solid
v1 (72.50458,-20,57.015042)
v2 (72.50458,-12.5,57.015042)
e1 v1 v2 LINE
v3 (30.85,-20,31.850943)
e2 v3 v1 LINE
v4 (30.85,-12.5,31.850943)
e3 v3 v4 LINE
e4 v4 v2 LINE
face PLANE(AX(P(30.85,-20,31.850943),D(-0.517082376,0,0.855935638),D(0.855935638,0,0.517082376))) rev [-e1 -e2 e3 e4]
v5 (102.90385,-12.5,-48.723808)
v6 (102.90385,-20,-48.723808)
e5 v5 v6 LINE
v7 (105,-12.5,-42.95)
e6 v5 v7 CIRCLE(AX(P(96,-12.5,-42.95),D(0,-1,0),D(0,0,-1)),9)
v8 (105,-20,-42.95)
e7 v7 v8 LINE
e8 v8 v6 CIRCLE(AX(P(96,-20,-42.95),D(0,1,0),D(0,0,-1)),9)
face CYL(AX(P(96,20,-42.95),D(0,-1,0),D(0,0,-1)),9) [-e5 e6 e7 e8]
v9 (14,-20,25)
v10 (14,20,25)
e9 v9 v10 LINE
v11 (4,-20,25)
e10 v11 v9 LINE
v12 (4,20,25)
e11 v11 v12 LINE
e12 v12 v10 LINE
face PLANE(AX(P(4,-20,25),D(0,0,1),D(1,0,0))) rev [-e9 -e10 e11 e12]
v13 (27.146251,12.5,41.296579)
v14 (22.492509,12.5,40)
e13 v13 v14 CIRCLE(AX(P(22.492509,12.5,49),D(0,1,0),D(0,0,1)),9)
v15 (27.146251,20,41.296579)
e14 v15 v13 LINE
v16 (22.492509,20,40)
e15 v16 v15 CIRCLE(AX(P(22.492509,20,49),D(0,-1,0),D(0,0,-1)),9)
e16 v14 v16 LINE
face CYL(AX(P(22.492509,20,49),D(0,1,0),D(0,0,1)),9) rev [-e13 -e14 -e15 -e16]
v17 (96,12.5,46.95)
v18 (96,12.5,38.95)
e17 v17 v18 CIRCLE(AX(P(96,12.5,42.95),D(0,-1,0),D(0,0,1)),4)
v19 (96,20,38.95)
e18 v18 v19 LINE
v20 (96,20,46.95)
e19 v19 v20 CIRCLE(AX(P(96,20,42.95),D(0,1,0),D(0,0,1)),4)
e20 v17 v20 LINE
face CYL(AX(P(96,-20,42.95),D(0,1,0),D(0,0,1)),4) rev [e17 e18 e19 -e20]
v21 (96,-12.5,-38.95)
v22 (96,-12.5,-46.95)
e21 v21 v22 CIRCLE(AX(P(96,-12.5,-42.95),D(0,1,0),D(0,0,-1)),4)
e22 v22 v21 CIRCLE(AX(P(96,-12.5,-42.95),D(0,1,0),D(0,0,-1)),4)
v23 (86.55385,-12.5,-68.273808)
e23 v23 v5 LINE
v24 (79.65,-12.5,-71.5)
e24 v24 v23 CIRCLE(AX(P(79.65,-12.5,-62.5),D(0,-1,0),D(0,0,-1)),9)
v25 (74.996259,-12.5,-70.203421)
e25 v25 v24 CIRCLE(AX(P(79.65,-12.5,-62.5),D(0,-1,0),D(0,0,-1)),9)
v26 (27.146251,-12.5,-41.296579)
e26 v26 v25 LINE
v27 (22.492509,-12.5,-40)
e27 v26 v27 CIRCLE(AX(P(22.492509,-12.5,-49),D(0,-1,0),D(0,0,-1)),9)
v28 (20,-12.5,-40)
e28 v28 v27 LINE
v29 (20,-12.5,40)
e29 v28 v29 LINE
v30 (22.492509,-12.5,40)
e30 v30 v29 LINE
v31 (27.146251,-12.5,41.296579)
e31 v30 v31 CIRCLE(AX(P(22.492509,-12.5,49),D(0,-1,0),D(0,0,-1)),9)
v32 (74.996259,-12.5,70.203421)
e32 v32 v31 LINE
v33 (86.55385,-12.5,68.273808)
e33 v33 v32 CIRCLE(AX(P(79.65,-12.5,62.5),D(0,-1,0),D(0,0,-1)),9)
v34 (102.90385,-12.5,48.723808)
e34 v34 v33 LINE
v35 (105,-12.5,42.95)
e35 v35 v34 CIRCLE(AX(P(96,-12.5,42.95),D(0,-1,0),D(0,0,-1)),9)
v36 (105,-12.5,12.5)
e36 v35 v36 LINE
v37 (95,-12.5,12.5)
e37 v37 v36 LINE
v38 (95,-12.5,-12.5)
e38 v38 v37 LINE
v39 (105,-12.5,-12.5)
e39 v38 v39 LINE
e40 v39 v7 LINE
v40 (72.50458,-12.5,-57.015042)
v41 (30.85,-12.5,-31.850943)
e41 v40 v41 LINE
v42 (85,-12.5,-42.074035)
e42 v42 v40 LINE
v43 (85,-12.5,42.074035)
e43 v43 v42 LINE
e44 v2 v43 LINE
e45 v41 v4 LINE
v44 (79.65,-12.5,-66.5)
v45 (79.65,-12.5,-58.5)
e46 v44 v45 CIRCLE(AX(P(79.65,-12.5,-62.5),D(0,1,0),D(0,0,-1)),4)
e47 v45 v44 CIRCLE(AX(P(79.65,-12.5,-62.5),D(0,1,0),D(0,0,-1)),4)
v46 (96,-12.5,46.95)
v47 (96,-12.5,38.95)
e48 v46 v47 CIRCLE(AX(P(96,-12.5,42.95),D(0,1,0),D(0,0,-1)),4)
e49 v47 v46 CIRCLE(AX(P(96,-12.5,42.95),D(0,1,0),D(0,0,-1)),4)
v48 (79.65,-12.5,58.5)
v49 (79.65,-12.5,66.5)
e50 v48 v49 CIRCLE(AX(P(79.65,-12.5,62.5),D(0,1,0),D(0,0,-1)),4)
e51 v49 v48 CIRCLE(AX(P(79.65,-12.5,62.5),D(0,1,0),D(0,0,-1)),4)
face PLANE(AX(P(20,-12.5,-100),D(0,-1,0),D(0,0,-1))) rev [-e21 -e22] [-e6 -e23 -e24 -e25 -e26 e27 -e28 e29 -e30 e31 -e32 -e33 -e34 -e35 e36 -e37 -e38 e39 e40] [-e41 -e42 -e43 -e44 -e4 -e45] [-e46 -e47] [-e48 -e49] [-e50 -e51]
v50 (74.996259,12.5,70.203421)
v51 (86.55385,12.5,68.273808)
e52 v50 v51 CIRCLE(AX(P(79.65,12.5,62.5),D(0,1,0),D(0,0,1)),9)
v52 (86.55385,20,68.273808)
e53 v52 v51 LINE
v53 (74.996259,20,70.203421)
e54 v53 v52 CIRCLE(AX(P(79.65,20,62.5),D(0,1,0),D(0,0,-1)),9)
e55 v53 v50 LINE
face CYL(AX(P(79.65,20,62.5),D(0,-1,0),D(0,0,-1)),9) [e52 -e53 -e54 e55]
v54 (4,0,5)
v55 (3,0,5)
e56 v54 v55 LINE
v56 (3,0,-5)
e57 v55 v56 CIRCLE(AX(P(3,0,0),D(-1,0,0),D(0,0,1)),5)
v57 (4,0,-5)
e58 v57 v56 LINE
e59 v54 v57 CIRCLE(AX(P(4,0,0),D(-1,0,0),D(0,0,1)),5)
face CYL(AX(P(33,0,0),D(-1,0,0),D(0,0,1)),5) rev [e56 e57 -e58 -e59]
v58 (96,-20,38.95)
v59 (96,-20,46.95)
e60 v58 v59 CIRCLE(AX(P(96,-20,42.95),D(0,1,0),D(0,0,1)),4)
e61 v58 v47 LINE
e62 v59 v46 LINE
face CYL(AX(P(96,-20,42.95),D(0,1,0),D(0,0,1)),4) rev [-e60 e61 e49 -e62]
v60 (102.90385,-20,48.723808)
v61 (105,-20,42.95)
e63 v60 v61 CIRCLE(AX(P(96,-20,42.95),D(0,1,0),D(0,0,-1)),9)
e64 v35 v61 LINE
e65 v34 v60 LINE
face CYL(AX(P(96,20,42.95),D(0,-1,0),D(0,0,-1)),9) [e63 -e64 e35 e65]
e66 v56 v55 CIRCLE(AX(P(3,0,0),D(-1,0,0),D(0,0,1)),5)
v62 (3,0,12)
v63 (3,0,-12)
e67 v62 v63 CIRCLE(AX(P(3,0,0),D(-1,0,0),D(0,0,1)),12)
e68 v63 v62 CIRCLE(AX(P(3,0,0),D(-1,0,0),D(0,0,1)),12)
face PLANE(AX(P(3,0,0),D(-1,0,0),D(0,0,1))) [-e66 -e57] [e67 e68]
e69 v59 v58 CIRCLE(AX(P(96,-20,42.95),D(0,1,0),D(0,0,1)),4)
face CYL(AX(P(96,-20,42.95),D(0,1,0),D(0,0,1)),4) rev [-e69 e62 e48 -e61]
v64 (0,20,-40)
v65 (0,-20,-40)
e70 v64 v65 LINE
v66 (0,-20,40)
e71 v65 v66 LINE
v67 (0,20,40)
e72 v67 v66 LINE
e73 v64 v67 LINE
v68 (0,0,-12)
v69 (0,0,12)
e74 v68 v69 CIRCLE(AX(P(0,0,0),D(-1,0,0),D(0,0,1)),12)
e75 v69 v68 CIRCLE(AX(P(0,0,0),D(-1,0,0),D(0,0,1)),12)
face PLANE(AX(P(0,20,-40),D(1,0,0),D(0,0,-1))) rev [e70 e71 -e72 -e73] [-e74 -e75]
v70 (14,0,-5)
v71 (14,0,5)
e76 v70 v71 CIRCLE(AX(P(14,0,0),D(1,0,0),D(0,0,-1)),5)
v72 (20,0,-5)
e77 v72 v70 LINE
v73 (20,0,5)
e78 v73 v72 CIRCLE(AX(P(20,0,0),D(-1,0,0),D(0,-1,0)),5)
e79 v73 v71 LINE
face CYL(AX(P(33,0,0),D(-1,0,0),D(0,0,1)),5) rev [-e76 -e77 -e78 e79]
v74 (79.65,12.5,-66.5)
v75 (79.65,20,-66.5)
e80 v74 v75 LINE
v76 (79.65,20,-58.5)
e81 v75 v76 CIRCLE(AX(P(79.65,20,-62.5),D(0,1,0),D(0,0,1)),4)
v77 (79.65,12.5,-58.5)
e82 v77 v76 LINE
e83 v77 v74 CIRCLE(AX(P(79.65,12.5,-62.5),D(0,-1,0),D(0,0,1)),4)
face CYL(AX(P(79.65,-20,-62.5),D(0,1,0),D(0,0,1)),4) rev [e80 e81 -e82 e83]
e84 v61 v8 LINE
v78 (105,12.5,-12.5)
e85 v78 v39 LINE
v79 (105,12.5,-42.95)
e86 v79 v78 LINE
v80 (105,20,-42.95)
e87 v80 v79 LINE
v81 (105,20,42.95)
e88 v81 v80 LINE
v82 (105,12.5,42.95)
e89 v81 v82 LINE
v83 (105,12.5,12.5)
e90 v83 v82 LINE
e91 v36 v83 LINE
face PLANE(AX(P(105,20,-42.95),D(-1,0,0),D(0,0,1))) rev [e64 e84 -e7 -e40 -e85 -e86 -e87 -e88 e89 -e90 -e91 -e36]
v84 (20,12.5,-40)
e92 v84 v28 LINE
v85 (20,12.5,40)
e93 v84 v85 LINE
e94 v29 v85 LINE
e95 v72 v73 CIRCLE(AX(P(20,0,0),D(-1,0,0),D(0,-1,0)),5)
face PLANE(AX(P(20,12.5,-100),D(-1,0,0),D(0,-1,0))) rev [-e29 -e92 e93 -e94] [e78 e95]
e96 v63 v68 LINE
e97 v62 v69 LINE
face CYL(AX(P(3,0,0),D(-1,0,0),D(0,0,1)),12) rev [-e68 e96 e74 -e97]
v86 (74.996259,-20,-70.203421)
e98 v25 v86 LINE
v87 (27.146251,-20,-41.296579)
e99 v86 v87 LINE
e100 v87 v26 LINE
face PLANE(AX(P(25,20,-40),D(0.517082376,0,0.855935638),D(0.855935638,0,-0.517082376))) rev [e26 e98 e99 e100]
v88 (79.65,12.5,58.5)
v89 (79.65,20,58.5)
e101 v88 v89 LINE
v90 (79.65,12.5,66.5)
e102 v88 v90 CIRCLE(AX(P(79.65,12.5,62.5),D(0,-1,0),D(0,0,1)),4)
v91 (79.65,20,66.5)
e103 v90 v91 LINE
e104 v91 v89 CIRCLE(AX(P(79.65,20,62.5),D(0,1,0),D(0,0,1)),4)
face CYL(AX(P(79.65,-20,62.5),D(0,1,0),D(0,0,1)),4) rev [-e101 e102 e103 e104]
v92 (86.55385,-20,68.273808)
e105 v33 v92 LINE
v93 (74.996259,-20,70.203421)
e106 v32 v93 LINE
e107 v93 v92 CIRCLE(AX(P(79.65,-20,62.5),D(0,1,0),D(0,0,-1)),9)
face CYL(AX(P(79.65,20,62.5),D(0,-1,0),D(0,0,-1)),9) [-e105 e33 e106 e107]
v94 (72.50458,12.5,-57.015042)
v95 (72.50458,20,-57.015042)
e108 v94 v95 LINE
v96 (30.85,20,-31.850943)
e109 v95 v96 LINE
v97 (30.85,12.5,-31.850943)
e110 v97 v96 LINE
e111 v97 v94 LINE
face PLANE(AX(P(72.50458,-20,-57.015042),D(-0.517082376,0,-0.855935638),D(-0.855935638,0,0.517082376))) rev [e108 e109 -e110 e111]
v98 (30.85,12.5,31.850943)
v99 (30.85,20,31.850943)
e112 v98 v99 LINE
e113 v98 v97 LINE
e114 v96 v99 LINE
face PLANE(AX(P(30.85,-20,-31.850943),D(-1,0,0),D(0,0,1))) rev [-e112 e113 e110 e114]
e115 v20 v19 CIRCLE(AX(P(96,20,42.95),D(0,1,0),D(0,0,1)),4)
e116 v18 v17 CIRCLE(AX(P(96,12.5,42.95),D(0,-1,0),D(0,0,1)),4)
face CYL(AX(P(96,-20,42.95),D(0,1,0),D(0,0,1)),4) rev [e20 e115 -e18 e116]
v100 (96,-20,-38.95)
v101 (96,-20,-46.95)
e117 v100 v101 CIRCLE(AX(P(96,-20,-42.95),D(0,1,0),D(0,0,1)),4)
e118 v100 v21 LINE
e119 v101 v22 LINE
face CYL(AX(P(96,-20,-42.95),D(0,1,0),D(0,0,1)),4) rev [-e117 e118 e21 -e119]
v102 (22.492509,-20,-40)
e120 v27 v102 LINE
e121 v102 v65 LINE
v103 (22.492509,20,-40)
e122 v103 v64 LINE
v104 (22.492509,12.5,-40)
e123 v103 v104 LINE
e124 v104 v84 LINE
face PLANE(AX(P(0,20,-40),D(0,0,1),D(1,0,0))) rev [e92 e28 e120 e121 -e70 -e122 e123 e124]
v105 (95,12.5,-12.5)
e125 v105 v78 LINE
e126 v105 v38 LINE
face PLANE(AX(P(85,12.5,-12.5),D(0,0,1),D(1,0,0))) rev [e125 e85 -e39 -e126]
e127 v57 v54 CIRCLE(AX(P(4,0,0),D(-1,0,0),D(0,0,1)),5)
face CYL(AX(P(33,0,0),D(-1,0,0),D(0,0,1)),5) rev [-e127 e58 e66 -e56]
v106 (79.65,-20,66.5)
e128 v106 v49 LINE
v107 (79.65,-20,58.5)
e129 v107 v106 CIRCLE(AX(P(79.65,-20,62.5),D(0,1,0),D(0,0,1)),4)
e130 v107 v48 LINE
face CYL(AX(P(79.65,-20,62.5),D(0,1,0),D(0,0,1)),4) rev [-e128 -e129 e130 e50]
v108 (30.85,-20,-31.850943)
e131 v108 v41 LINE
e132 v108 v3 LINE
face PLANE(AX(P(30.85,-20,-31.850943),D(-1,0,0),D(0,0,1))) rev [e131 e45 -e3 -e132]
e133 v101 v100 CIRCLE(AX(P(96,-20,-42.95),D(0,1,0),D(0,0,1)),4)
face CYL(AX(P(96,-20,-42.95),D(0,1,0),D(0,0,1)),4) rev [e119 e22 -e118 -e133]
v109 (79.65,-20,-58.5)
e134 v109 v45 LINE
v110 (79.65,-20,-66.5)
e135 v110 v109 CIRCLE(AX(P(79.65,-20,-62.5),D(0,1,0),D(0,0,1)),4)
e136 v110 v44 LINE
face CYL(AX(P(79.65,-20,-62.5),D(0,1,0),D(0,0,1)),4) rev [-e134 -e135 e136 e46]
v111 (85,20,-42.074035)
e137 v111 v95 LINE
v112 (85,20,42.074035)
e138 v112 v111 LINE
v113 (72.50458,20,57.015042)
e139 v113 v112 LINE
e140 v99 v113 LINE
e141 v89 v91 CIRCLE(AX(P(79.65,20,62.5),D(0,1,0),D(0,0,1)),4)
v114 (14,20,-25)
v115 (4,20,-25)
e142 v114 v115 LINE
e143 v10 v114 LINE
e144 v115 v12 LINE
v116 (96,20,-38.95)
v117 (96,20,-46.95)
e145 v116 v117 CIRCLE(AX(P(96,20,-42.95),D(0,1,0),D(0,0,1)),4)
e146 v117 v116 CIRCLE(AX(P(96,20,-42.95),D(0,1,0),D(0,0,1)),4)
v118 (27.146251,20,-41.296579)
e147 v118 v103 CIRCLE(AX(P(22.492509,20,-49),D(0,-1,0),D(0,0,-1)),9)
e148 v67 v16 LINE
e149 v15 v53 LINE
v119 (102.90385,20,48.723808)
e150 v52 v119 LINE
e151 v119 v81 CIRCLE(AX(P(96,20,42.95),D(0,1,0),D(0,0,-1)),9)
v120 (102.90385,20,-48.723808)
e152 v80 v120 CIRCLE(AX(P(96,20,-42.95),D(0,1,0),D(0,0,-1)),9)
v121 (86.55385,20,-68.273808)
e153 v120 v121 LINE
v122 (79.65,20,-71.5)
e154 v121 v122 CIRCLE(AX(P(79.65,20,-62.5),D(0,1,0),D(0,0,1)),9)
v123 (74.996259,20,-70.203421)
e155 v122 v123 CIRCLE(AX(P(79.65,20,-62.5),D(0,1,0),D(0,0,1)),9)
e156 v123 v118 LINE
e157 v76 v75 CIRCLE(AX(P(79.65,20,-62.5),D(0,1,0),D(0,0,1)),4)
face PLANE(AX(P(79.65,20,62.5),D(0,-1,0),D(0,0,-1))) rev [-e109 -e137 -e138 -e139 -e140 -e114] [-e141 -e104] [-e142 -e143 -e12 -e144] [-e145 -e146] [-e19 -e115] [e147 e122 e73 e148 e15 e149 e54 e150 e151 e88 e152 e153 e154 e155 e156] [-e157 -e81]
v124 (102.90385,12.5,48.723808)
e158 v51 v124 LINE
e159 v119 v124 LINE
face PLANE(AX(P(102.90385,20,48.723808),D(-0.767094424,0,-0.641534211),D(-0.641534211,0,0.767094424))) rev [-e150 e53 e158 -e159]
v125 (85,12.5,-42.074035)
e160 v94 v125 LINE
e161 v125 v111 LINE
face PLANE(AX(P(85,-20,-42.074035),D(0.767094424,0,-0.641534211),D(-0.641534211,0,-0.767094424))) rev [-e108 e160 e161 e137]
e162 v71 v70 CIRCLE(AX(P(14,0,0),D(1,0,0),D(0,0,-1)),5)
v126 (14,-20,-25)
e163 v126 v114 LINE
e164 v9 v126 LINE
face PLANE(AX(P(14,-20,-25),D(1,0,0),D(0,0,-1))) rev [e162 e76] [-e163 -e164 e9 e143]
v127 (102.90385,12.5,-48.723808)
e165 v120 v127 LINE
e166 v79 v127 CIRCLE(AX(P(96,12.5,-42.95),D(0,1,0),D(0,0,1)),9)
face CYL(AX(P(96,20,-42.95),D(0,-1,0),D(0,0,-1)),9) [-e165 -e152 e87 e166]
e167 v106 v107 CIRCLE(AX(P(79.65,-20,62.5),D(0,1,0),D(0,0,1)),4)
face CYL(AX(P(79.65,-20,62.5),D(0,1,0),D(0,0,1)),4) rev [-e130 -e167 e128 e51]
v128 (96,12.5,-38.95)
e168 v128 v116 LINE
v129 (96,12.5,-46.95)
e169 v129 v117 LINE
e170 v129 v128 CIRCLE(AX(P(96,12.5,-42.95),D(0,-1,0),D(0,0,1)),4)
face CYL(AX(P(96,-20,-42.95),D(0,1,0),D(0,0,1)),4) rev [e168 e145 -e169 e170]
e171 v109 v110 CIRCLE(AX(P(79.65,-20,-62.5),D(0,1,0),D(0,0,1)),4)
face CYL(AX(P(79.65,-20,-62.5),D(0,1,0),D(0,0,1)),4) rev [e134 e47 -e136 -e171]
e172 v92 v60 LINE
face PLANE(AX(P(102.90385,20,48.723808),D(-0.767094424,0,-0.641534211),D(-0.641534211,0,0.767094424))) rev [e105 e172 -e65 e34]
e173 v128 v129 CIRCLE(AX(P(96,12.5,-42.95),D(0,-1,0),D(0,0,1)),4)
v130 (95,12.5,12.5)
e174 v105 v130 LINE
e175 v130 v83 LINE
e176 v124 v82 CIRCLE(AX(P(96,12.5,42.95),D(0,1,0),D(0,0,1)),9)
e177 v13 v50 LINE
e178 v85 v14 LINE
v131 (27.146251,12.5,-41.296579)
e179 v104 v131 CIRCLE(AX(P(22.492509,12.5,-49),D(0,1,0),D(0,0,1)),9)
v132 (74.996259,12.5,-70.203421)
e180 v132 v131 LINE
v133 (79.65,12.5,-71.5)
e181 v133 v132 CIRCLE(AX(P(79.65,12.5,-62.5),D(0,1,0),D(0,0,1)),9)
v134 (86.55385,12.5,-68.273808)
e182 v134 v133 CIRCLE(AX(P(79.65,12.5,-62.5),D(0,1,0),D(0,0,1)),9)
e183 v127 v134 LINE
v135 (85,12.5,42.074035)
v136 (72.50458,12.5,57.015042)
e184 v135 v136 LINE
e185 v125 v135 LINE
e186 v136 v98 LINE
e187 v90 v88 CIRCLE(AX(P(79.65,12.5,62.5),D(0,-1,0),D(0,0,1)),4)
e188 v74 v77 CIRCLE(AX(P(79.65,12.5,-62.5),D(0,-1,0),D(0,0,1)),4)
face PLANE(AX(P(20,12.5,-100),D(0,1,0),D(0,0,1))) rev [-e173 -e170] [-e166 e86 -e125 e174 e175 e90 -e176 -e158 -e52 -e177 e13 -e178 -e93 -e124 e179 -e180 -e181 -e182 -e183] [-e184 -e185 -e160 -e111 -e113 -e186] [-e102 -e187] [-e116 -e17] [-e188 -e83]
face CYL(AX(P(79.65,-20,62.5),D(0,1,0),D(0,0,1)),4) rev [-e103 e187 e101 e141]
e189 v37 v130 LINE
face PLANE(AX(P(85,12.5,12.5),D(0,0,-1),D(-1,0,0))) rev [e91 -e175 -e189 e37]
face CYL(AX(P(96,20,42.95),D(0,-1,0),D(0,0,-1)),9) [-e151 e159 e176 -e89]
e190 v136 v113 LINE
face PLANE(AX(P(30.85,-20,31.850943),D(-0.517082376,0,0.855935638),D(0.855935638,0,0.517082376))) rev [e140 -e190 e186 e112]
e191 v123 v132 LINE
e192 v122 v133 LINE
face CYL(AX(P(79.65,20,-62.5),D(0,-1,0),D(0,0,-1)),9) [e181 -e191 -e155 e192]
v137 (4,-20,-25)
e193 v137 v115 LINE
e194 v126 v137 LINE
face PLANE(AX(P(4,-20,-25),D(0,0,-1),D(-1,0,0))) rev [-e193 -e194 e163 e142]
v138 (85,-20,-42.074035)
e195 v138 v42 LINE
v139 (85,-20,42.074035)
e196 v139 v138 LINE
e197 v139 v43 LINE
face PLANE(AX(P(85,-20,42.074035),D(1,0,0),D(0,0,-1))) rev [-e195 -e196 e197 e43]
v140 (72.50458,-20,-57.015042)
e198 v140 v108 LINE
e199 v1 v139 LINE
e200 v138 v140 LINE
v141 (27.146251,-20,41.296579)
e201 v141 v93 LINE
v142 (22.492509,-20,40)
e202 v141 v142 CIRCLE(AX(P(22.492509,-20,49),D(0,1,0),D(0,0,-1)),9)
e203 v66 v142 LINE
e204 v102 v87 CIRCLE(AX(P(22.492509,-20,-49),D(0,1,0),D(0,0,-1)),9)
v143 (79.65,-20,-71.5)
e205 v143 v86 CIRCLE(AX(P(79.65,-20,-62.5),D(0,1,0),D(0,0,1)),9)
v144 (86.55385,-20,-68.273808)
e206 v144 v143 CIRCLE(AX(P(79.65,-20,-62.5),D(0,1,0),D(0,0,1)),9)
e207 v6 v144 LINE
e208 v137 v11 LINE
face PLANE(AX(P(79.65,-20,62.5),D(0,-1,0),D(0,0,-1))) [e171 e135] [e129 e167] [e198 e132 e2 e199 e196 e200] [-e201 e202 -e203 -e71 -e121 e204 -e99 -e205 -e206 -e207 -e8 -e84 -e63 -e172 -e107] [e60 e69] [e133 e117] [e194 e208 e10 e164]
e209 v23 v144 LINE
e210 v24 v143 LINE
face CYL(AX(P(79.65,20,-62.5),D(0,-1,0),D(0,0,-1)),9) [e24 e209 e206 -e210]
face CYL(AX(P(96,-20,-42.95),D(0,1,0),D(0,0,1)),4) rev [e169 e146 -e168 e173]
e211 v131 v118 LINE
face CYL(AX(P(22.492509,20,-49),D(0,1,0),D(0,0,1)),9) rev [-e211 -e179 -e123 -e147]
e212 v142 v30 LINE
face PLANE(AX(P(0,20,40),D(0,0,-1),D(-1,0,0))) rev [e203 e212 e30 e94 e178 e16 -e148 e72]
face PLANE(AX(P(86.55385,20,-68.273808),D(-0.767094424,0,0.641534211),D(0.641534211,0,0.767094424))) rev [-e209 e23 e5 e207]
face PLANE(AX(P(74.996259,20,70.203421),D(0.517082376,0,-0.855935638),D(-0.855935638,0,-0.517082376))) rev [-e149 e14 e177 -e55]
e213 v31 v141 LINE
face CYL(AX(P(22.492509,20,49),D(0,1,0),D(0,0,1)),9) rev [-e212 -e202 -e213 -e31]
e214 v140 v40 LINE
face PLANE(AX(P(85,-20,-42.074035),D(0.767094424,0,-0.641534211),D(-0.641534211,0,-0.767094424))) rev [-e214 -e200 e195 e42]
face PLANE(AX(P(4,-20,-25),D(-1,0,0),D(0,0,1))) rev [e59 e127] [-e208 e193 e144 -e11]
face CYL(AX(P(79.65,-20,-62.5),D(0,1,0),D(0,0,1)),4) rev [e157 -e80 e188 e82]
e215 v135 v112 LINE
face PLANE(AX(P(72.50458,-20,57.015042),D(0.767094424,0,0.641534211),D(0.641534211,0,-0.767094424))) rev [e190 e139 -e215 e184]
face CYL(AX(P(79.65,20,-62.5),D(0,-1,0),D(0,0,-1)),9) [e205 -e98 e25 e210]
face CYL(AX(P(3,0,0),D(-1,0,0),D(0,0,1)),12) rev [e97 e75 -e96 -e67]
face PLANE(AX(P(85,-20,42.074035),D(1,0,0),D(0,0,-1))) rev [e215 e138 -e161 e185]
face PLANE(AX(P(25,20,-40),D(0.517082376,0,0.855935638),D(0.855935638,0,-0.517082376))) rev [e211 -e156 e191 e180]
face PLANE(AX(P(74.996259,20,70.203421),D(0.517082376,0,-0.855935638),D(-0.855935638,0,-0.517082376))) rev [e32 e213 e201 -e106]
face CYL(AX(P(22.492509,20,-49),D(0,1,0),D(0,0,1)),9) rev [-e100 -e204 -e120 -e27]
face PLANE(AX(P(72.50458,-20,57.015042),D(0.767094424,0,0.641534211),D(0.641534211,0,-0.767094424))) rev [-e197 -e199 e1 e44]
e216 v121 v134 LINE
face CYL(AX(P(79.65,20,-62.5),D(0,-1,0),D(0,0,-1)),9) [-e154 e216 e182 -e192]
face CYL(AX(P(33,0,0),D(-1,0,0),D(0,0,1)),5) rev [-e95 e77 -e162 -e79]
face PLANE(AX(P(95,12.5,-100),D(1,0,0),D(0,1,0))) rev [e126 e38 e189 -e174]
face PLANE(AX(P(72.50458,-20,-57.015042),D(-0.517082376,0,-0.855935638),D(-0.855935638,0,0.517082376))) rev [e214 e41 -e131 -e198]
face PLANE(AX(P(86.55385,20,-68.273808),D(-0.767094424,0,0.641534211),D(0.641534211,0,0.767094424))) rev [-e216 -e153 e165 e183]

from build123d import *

# Parameters (mm, degrees)
FRAME_BODY_DEPTH                  = 20
WINDOW_AND_HOLES_SKETCH_R         = 4
WINDOW_AND_HOLES_SKETCH_W         = 10
WINDOW_AND_HOLES_SKETCH_H         = 50
WINDOW_AND_FIXING_HOLES_CUT_DEPTH = 20
SIDE_SLOT_SKETCH_W                = 75
SIDE_SLOT_SKETCH_H                = 25
SIDE_SLOT_CUT_DEPTH               = 100
TOP_SLOT_SKETCH_W                 = 59
TOP_SLOT_SKETCH_H                 = 25
TOP_SLOT_CUT_DEPTH                = 20
COUNTERBORE_24_SKETCH_R           = 12
COUNTERBORE_24_DEPTH              = 3
HOLE_10_SKETCH_R                  = 5
HOLE_10_DEPTH                     = 30
CORNER_FILLETS_R9_R               = 9


with BuildPart() as part:
    # Frame Profile Sketch → Frame Body (new, symmetric)
    with BuildSketch(Plane(origin=(0, 0, 0), x_dir=(1, 0, 0), z_dir=(0, 1, 0))):
        with BuildLine():
            Line((25, 40), (74.996258615, 70.203420742))
            ThreePointArc((74.996258615, 70.203420742), (81.13209258, 71.377128003), (86.553849817, 68.273807903))
            Line((86.553849817, 68.273807903), (102.903849817, 48.723807903))
            ThreePointArc((102.903849817, 48.723807903), (104.459747288, 46.02126616), (105, 42.95))
            Line((105, 42.95), (105, -42.95))
            ThreePointArc((105, -42.95), (104.459747288, -46.02126616), (102.903849817, -48.723807903))
            Line((102.903849817, -48.723807903), (86.553849817, -68.273807903))
            ThreePointArc((86.553849817, -68.273807903), (81.13209258, -71.377128003), (74.996258615, -70.203420742))
            Line((74.996258615, -70.203420742), (25, -40))
            Line((25, -40), (0, -40))
            Line((0, -40), (0, 40))
            Line((0, 40), (25, 40))
        make_face()
    extrude(amount=FRAME_BODY_DEPTH, both=True)

    # Window and Holes Sketch → Window and Fixing Holes Cut (cut, symmetric)
    with BuildSketch(Plane(origin=(0, 0, 0), x_dir=(1, 0, 0), z_dir=(0, 1, 0))):
        with Locations(Location((79.65, 62.5, 0), (0, 0, 270))):
            Circle(WINDOW_AND_HOLES_SKETCH_R)
        with Locations(Location((96, 42.95, 0), (0, 0, 270))):
            Circle(WINDOW_AND_HOLES_SKETCH_R)
        with Locations(Location((96, -42.95, 0), (0, 0, 270))):
            Circle(WINDOW_AND_HOLES_SKETCH_R)
        with Locations(Location((79.65, -62.5, 0), (0, 0, 270))):
            Circle(WINDOW_AND_HOLES_SKETCH_R)
        Polygon((30.85, 31.850943236), (30.85, -31.850943236), (72.504579862, -57.015042236), (85, -42.074035282), (85, 42.074035282), (72.504579862, 57.015042236), align=None)
        with Locations((9, 0)):
            Rectangle(WINDOW_AND_HOLES_SKETCH_W, WINDOW_AND_HOLES_SKETCH_H)
    extrude(amount=WINDOW_AND_FIXING_HOLES_CUT_DEPTH, both=True, mode=Mode.SUBTRACT)

    # Side Slot Sketch → Side Slot Cut (cut, symmetric)
    with BuildSketch(Plane.XY):
        with Locations((57.5, 0)):
            Rectangle(SIDE_SLOT_SKETCH_W, SIDE_SLOT_SKETCH_H)
    extrude(amount=SIDE_SLOT_CUT_DEPTH, both=True, mode=Mode.SUBTRACT)

    # Top Slot Sketch → Top Slot Cut (cut)
    with BuildSketch(Plane(origin=(105, 0, 0), x_dir=(0, 0, -1), z_dir=(1, 0, 0))):
        with Locations((-42, 0)):
            Rectangle(TOP_SLOT_SKETCH_W, TOP_SLOT_SKETCH_H)
        with Locations((42, 0)):
            Rectangle(TOP_SLOT_SKETCH_W, TOP_SLOT_SKETCH_H)
    extrude(amount=-TOP_SLOT_CUT_DEPTH, mode=Mode.SUBTRACT)

    # Counterbore Ø24 Sketch → Counterbore Ø24 (cut)
    with BuildSketch(Plane.ZY):
        Circle(COUNTERBORE_24_SKETCH_R)
    extrude(amount=-COUNTERBORE_24_DEPTH, mode=Mode.SUBTRACT)

    # Hole Ø10 Sketch → Hole Ø10 (cut)
    with BuildSketch(Plane.ZY.offset(-3)):
        with Locations(Location((0, 0, 0), (0, 0, 270))):
            Circle(HOLE_10_SKETCH_R)
    extrude(amount=-HOLE_10_DEPTH, mode=Mode.SUBTRACT)

    # Corner Fillets R9
    corner_fillets_r9_edges = [part.edges().sort_by_distance(p)[0] for p in [
        (25, -16.25, -40),
        (25, -16.25, 40),
        (25, 16.25, -40),
        (25, 16.25, 40),
    ]]
    fillet(corner_fillets_r9_edges, radius=CORNER_FILLETS_R9_R)


solid = part.part
